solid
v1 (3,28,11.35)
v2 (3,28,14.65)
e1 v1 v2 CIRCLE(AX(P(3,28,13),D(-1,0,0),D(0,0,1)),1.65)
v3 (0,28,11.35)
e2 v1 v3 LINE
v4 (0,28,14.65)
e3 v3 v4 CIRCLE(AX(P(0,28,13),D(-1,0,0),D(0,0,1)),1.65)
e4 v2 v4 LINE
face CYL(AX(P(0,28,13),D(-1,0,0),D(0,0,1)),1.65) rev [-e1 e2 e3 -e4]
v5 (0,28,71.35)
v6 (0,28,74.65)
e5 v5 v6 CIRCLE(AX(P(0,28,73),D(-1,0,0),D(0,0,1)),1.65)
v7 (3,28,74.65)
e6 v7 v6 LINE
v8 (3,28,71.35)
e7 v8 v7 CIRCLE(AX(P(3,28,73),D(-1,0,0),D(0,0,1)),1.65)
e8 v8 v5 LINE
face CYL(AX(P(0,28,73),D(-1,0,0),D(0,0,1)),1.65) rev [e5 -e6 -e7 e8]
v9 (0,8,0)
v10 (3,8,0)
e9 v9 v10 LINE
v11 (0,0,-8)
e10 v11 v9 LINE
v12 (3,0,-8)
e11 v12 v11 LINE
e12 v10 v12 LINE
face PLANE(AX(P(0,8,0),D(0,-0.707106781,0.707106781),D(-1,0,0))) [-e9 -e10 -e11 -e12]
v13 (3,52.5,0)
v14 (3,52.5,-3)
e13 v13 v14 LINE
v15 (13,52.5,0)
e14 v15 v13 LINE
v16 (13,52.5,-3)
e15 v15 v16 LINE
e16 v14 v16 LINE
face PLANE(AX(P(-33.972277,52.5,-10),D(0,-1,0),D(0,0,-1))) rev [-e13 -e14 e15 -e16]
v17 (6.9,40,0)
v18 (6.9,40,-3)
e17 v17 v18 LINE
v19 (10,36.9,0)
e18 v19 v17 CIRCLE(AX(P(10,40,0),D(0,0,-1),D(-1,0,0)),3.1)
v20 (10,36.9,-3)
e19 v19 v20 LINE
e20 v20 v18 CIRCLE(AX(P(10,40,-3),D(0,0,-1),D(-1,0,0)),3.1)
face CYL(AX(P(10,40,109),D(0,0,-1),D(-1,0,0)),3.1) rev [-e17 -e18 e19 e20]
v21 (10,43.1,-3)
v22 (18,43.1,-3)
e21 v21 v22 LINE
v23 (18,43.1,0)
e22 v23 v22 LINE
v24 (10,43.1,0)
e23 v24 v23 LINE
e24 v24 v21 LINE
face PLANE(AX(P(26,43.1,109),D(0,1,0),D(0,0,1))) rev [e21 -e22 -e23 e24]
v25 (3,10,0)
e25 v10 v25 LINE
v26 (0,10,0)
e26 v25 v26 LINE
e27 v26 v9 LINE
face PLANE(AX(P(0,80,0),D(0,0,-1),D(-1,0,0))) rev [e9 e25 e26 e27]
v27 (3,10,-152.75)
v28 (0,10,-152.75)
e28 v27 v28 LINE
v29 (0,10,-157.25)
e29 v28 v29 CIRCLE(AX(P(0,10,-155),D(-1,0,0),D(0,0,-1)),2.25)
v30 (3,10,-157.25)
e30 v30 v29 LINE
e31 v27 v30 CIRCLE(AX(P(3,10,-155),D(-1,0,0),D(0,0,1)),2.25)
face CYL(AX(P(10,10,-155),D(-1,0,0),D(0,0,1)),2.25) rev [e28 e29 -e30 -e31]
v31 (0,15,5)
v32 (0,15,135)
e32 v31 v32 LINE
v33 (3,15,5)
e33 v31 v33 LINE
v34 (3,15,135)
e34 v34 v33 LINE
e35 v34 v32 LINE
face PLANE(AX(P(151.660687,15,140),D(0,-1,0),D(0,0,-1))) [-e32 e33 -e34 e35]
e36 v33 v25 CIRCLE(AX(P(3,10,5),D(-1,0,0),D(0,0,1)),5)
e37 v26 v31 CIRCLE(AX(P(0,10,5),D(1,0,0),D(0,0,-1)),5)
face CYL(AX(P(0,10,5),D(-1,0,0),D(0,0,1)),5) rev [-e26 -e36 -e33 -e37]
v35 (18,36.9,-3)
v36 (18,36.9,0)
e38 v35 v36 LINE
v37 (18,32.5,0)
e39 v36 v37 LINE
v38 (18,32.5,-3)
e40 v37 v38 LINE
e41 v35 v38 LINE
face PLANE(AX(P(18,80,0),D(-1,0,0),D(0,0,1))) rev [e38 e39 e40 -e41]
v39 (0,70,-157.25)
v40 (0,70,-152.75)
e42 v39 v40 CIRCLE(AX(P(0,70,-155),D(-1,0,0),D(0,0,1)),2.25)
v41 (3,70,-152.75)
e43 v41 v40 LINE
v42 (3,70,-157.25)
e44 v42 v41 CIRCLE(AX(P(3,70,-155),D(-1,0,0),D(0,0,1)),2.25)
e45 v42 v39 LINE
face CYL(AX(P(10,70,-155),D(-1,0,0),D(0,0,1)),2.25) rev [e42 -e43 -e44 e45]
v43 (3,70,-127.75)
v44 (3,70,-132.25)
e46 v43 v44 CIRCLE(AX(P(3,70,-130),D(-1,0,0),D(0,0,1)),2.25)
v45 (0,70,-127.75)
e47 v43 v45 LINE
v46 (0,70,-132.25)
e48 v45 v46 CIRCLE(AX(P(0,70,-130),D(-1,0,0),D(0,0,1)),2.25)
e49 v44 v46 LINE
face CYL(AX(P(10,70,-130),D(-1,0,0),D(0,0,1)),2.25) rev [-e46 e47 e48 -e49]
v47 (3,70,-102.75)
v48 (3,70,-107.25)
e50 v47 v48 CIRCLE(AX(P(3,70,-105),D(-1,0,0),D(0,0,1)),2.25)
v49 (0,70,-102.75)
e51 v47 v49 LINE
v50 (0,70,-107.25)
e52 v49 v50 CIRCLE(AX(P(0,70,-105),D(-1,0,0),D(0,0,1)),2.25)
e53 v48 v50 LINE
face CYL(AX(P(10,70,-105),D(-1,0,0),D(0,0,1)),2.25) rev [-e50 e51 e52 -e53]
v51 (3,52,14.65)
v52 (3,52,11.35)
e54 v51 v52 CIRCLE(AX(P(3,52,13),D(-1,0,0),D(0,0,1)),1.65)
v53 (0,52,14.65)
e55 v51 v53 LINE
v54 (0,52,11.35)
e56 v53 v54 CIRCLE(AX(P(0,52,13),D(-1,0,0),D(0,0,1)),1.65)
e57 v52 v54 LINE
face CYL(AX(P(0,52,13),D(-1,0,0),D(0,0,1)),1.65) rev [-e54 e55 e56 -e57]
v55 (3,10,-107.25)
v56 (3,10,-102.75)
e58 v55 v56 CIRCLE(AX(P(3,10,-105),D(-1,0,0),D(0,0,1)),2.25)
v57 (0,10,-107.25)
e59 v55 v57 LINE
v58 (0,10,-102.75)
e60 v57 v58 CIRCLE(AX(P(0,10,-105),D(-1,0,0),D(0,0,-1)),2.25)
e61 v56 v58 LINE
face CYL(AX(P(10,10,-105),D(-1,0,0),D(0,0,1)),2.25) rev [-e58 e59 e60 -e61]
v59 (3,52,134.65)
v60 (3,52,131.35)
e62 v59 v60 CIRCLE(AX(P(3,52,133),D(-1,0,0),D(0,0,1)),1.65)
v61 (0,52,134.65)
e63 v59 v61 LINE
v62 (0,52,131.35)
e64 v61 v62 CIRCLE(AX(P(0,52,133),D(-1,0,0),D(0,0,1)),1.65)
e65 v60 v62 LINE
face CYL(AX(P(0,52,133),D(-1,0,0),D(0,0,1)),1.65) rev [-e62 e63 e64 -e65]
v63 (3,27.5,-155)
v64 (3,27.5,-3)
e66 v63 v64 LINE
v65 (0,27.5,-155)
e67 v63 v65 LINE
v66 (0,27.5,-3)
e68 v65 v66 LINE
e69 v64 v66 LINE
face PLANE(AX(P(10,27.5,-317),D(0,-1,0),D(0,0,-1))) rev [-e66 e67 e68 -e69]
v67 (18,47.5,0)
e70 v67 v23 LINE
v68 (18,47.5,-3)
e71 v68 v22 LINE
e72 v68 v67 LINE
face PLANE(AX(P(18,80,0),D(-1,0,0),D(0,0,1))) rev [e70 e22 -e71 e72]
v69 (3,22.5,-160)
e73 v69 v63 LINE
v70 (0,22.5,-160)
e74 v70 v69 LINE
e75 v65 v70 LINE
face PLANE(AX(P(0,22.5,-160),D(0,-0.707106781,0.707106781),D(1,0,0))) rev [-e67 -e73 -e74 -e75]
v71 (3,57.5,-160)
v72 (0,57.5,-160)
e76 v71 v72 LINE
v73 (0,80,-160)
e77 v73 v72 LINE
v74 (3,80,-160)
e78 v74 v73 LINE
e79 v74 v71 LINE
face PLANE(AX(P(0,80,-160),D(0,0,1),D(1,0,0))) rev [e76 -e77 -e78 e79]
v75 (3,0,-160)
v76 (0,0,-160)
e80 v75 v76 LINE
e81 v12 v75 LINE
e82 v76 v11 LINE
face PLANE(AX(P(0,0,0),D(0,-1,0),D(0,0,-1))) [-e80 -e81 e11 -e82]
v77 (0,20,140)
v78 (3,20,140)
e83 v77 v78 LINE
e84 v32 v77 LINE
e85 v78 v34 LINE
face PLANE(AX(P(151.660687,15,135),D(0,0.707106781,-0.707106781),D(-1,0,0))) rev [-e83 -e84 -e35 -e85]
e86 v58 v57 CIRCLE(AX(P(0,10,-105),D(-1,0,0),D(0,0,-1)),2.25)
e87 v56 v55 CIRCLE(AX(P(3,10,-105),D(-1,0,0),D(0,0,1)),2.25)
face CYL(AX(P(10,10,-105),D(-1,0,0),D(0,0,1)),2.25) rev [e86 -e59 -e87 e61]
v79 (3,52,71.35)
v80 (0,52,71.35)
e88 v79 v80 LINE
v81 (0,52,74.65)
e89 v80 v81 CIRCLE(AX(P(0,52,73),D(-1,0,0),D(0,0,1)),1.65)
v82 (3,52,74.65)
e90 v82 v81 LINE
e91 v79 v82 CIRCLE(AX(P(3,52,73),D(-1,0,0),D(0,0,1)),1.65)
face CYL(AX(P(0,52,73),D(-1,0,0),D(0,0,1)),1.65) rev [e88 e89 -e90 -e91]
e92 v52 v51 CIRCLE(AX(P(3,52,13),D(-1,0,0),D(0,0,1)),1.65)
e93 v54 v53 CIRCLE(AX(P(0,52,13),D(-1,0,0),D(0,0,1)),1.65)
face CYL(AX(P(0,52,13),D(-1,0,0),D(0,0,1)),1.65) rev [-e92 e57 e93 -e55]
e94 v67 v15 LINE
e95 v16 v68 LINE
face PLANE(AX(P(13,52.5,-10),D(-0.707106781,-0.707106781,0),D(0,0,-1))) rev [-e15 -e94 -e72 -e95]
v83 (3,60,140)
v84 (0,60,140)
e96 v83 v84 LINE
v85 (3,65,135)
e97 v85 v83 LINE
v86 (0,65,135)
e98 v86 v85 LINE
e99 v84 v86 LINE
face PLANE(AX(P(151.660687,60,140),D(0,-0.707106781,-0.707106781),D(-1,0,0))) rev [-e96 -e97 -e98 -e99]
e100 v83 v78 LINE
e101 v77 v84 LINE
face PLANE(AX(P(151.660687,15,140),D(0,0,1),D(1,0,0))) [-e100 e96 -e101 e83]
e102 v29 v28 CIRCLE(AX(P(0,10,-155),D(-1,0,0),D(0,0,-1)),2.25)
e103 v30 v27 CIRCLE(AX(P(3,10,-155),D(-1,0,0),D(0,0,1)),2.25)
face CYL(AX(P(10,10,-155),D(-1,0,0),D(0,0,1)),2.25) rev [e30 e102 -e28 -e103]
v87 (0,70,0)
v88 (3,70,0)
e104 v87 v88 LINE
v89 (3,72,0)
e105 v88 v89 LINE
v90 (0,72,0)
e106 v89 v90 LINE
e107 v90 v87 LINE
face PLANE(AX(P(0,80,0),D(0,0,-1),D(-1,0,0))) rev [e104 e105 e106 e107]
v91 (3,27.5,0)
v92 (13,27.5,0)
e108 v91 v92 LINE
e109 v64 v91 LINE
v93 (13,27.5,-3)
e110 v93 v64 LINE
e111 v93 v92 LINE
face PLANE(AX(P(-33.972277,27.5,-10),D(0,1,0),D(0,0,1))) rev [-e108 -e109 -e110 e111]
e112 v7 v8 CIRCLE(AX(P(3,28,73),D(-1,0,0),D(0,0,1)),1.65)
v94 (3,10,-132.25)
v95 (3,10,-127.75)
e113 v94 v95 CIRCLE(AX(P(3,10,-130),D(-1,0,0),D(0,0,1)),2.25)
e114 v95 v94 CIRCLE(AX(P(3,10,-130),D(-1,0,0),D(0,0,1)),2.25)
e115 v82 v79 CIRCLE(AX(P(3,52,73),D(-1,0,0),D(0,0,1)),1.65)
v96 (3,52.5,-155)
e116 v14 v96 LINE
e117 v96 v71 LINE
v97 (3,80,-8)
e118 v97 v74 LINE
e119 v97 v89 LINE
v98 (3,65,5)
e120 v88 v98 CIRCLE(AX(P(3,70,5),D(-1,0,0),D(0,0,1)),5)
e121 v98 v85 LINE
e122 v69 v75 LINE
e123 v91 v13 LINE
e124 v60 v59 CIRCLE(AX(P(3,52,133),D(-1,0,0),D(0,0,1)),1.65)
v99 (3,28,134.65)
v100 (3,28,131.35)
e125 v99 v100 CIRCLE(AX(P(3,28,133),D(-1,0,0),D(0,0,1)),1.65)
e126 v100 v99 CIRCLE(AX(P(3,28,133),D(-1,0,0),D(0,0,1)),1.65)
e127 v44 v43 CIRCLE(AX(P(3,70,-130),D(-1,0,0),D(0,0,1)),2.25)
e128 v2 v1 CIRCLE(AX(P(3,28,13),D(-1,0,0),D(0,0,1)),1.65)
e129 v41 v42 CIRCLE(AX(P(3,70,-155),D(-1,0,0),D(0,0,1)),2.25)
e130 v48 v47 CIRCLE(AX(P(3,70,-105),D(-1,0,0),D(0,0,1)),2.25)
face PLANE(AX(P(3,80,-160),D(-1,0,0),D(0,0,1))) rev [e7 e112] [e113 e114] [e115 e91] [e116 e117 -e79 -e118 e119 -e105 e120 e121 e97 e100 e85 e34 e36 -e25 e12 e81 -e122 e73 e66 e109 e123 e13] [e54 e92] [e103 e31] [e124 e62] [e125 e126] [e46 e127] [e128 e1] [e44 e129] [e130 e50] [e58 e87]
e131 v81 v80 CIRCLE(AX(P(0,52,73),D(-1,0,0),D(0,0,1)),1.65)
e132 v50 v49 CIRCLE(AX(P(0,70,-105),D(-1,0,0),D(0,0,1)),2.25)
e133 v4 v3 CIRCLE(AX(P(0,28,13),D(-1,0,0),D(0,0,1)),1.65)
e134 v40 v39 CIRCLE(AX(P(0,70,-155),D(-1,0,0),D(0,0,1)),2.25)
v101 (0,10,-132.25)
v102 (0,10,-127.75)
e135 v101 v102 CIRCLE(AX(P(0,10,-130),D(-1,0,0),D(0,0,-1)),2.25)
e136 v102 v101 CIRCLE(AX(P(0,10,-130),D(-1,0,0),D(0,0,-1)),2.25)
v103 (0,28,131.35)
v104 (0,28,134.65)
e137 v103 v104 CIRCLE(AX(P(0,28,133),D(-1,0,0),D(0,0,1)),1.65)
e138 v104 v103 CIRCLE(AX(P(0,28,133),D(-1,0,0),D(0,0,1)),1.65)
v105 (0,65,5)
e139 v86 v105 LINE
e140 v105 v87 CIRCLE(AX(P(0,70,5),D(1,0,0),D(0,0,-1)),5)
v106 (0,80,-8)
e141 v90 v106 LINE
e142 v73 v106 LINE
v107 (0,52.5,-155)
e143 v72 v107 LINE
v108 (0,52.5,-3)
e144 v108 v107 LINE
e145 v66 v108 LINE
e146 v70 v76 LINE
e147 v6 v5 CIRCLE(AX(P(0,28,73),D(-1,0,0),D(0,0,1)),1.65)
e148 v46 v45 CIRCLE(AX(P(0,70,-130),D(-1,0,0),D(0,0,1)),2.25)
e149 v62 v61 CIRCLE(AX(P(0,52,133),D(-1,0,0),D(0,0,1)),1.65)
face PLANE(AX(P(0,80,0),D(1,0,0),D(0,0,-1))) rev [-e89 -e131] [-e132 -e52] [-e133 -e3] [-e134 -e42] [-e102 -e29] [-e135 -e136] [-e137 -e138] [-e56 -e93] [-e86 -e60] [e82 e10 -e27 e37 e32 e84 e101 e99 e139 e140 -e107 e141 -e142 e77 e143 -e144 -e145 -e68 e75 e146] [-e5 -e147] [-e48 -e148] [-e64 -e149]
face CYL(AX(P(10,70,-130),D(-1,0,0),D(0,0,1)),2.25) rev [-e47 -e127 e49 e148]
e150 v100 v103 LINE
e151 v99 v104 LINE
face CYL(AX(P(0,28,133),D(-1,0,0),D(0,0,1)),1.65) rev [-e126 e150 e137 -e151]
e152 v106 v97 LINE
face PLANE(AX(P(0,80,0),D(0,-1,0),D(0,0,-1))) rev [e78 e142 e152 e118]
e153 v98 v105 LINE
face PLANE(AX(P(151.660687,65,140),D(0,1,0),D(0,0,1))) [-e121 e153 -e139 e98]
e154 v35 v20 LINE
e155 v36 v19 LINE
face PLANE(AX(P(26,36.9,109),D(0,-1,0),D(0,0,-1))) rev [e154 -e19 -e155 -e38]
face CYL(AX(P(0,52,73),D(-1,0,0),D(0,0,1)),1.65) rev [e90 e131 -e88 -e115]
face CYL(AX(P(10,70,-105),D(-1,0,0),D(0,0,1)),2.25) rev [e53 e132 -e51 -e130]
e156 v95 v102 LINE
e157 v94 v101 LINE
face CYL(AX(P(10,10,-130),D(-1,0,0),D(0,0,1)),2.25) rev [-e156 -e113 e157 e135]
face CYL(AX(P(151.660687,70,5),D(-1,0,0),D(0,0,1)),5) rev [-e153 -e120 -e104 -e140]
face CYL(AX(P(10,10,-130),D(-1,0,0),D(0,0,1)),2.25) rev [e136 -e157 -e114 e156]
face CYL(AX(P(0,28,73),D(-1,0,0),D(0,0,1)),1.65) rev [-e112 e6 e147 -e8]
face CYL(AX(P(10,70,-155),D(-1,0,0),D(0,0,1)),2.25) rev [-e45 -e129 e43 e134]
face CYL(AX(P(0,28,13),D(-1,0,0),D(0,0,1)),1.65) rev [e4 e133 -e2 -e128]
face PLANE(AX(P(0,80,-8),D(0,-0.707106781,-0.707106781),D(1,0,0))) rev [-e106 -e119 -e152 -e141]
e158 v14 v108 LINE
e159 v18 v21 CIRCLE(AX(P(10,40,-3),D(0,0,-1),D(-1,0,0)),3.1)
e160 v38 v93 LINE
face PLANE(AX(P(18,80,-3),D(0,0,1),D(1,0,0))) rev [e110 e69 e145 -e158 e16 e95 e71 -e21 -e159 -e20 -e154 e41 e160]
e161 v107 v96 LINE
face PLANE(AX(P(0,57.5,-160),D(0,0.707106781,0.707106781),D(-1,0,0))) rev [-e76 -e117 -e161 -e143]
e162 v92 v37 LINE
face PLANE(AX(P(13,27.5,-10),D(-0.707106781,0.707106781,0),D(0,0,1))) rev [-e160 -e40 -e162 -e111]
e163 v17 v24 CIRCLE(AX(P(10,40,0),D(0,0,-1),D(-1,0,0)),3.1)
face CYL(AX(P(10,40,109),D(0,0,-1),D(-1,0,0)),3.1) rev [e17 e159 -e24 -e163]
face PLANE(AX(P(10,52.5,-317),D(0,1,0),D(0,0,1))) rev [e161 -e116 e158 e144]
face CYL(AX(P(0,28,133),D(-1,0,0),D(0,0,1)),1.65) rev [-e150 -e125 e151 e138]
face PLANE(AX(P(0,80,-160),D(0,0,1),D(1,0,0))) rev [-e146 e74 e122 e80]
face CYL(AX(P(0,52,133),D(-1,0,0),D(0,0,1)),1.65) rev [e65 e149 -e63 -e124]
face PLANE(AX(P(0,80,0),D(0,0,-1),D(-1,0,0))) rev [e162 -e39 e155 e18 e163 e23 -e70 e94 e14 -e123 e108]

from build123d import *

# Parameters (mm, degrees)
BOSS_EXTRUDE1_DEPTH        = 80
SKETCH2_R                  = 2.75
CUT_EXTRUDE1_DEPTH         = 10
SKETCH3_W                  = 314
SKETCH3_H                  = 25
CUT_EXTRUDE2_DEPTH         = 10
SKETCH4_W                  = 140
SKETCH4_H                  = 50
BOSS_EXTRUDE2_DEPTH        = 3
SKETCH5_W                  = 24.712329927
SKETCH5_H                  = 27.5
CUT_EXTRUDE3_DEPTH         = 15
CHAMFER1_SIZE              = 5
CHAMFER2_SIZE              = 8
CUT_EXTRUDE4_DEPTH         = 112
SKETCH9_R                  = 1
CUT_EXTRUDE5_DEPTH         = 10
M4_TAPPED_HOLE1_AT_2_COUNT = 2
M4_TAPPED_HOLE1_AT_2_PITCH = 24
LPATTERN1_COUNT            = 3
LPATTERN1_PITCH            = 60
SKETCH11_R                 = 2.25
CUT_EXTRUDE6_DEPTH         = 10
LPATTERN2_COUNT            = 3
LPATTERN2_PITCH            = 25
CHAMFER3_SIZE              = 5
CHAMFER4_SIZE              = 5
FILLET1_R                  = 5


with BuildPart() as part:
    # Sketch1 → Boss-Extrude1 (new body)
    with BuildSketch(Plane(origin=(0, 0, 0), x_dir=(1, 0, 0), z_dir=(0, 1, 0))):
        Polygon((0, 0), (18, 0), (18, 3), (3, 3), (3, 160), (0, 160), align=None)
    extrude(amount=BOSS_EXTRUDE1_DEPTH)

    # Sketch2 → Cut-Extrude1 (cut)
    with BuildSketch(Plane.XY):
        with Locations((10, 40)):
            Circle(SKETCH2_R)
    extrude(amount=-CUT_EXTRUDE1_DEPTH, mode=Mode.SUBTRACT)

    # Sketch3 → Cut-Extrude2 (cut)
    with BuildSketch(Plane.ZY):
        with Locations((-160, 40)):
            Rectangle(SKETCH3_W, SKETCH3_H)
    extrude(amount=-CUT_EXTRUDE2_DEPTH, mode=Mode.SUBTRACT)

    # Sketch4 → Boss-Extrude2 (add)
    with BuildSketch(Plane.ZY):
        with Locations((70, 40)):
            Rectangle(SKETCH4_W, SKETCH4_H)
    extrude(amount=-BOSS_EXTRUDE2_DEPTH)

    # Sketch5 → Cut-Extrude3 (cut)
    with BuildSketch(Plane(origin=(18, 0, 0), x_dir=(0, 0, -1), z_dir=(1, 0, 0))):
        with Locations((-2.356164964, 13.75)):
            Rectangle(SKETCH5_W, SKETCH5_H)
        with Locations((-2.356164964, 66.25)):
            Rectangle(SKETCH5_W, SKETCH5_H)
    extrude(amount=-CUT_EXTRUDE3_DEPTH, mode=Mode.SUBTRACT)

    # Chamfer1
    chamfer1_edges = [part.edges().sort_by_distance(p)[0] for p in [
        (18, 27.5, -1.5),
        (18, 52.5, -1.5),
    ]]
    chamfer(chamfer1_edges, length=CHAMFER1_SIZE)

    # Chamfer2
    chamfer2_edges = [part.edges().sort_by_distance(p)[0] for p in [
        (1.5, 0, 0),
        (1.5, 80, 0),
    ]]
    chamfer(chamfer2_edges, length=CHAMFER2_SIZE)

    # Sketch8 → Cut-Extrude4 (cut)
    with BuildSketch(Plane(origin=(0, 0, -3), x_dir=(-1, 0, 0), z_dir=(0, 0, -1))):
        with BuildLine():
            Line((-26, 43.1), (-10, 43.1))
            ThreePointArc((-10, 43.1), (-6.9, 40), (-10, 36.9))
            Line((-10, 36.9), (-26, 36.9))
            ThreePointArc((-26, 36.9), (-29.1, 40), (-26, 43.1))
        make_face()
    extrude(amount=-CUT_EXTRUDE4_DEPTH, mode=Mode.SUBTRACT)

    # Sketch9 → Cut-Extrude5 (cut)
    with BuildSketch(Plane.ZY):
        with Locations((133, 52)):
            Circle(SKETCH9_R)
        with Locations((133, 28)):
            Circle(SKETCH9_R)
    extrude(amount=-CUT_EXTRUDE5_DEPTH, mode=Mode.SUBTRACT)

    # Sketch10 → M4 Tapped Hole1 (revolve, cut)
    with BuildSketch(Plane(origin=(0, 52, 133), x_dir=(0, 0, 1), z_dir=(0, 1, 0))):
        Polygon((0, 0), (0, 11.091420021), (1.65, 10.1), (1.65, 0), align=None)
    m4_tapped_hole1 = revolve(axis=Axis((-6.35, 52, 133), (1, 0, 0)), mode=Mode.SUBTRACT)

    # M4 Tapped Hole1 at 2: M4 Tapped Hole1 ×2
    with Locations(*[(0, -i * M4_TAPPED_HOLE1_AT_2_PITCH, 0) for i in range(1, M4_TAPPED_HOLE1_AT_2_COUNT)]):
        add(m4_tapped_hole1, mode=Mode.SUBTRACT)

    # LPattern1: M4 Tapped Hole1 ×3
    with Locations(*[(0, 0, -i * LPATTERN1_PITCH) for i in range(1, LPATTERN1_COUNT)]):
        add(m4_tapped_hole1, mode=Mode.SUBTRACT)

    # LPattern1 copy 1 sketch → LPattern1 copy 1 (revolve, cut)
    with BuildSketch(Plane(origin=(0, 28, 73), x_dir=(0, 0, 1), z_dir=(0, 1, 0))):
        Polygon((0, 0), (0, 11.091420021), (1.65, 10.1), (1.65, 0), align=None)
    revolve(axis=Axis((-6.35, 28, 73), (1, 0, 0)), mode=Mode.SUBTRACT)

    # LPattern1 copy 2 sketch → LPattern1 copy 2 (revolve, cut)
    with BuildSketch(Plane(origin=(0, 28, 13), x_dir=(0, 0, 1), z_dir=(0, 1, 0))):
        Polygon((0, 0), (0, 11.091420021), (1.65, 10.1), (1.65, 0), align=None)
    revolve(axis=Axis((-6.35, 28, 13), (1, 0, 0)), mode=Mode.SUBTRACT)

    # Sketch11 → Cut-Extrude6 (cut)
    with BuildSketch(Plane.ZY):
        with Locations((-155, 70)):
            Circle(SKETCH11_R)
        with Locations((-155, 10)):
            Circle(SKETCH11_R)
    cut_extrude6 = extrude(amount=-CUT_EXTRUDE6_DEPTH, mode=Mode.SUBTRACT)

    # LPattern2: Cut-Extrude6 ×3
    with Locations(*[(0, 0, i * LPATTERN2_PITCH) for i in range(1, LPATTERN2_COUNT)]):
        add(cut_extrude6, mode=Mode.SUBTRACT)

    # Chamfer3
    chamfer3_edges = [part.edges().sort_by_distance(p)[0] for p in [
        (1.5, 52.5, -160),
        (1.5, 27.5, -160),
    ]]
    chamfer(chamfer3_edges, length=CHAMFER3_SIZE)

    # Chamfer4
    chamfer4_edges = [part.edges().sort_by_distance(p)[0] for p in [
        (1.5, 15, 140),
        (1.5, 65, 140),
    ]]
    chamfer(chamfer4_edges, length=CHAMFER4_SIZE)

    # Fillet1
    fillet1_edges = [part.edges().sort_by_distance(p)[0] for p in [
        (1.5, 15, 0),
        (1.5, 65, 0),
    ]]
    fillet(fillet1_edges, radius=FILLET1_R)


solid = part.part
